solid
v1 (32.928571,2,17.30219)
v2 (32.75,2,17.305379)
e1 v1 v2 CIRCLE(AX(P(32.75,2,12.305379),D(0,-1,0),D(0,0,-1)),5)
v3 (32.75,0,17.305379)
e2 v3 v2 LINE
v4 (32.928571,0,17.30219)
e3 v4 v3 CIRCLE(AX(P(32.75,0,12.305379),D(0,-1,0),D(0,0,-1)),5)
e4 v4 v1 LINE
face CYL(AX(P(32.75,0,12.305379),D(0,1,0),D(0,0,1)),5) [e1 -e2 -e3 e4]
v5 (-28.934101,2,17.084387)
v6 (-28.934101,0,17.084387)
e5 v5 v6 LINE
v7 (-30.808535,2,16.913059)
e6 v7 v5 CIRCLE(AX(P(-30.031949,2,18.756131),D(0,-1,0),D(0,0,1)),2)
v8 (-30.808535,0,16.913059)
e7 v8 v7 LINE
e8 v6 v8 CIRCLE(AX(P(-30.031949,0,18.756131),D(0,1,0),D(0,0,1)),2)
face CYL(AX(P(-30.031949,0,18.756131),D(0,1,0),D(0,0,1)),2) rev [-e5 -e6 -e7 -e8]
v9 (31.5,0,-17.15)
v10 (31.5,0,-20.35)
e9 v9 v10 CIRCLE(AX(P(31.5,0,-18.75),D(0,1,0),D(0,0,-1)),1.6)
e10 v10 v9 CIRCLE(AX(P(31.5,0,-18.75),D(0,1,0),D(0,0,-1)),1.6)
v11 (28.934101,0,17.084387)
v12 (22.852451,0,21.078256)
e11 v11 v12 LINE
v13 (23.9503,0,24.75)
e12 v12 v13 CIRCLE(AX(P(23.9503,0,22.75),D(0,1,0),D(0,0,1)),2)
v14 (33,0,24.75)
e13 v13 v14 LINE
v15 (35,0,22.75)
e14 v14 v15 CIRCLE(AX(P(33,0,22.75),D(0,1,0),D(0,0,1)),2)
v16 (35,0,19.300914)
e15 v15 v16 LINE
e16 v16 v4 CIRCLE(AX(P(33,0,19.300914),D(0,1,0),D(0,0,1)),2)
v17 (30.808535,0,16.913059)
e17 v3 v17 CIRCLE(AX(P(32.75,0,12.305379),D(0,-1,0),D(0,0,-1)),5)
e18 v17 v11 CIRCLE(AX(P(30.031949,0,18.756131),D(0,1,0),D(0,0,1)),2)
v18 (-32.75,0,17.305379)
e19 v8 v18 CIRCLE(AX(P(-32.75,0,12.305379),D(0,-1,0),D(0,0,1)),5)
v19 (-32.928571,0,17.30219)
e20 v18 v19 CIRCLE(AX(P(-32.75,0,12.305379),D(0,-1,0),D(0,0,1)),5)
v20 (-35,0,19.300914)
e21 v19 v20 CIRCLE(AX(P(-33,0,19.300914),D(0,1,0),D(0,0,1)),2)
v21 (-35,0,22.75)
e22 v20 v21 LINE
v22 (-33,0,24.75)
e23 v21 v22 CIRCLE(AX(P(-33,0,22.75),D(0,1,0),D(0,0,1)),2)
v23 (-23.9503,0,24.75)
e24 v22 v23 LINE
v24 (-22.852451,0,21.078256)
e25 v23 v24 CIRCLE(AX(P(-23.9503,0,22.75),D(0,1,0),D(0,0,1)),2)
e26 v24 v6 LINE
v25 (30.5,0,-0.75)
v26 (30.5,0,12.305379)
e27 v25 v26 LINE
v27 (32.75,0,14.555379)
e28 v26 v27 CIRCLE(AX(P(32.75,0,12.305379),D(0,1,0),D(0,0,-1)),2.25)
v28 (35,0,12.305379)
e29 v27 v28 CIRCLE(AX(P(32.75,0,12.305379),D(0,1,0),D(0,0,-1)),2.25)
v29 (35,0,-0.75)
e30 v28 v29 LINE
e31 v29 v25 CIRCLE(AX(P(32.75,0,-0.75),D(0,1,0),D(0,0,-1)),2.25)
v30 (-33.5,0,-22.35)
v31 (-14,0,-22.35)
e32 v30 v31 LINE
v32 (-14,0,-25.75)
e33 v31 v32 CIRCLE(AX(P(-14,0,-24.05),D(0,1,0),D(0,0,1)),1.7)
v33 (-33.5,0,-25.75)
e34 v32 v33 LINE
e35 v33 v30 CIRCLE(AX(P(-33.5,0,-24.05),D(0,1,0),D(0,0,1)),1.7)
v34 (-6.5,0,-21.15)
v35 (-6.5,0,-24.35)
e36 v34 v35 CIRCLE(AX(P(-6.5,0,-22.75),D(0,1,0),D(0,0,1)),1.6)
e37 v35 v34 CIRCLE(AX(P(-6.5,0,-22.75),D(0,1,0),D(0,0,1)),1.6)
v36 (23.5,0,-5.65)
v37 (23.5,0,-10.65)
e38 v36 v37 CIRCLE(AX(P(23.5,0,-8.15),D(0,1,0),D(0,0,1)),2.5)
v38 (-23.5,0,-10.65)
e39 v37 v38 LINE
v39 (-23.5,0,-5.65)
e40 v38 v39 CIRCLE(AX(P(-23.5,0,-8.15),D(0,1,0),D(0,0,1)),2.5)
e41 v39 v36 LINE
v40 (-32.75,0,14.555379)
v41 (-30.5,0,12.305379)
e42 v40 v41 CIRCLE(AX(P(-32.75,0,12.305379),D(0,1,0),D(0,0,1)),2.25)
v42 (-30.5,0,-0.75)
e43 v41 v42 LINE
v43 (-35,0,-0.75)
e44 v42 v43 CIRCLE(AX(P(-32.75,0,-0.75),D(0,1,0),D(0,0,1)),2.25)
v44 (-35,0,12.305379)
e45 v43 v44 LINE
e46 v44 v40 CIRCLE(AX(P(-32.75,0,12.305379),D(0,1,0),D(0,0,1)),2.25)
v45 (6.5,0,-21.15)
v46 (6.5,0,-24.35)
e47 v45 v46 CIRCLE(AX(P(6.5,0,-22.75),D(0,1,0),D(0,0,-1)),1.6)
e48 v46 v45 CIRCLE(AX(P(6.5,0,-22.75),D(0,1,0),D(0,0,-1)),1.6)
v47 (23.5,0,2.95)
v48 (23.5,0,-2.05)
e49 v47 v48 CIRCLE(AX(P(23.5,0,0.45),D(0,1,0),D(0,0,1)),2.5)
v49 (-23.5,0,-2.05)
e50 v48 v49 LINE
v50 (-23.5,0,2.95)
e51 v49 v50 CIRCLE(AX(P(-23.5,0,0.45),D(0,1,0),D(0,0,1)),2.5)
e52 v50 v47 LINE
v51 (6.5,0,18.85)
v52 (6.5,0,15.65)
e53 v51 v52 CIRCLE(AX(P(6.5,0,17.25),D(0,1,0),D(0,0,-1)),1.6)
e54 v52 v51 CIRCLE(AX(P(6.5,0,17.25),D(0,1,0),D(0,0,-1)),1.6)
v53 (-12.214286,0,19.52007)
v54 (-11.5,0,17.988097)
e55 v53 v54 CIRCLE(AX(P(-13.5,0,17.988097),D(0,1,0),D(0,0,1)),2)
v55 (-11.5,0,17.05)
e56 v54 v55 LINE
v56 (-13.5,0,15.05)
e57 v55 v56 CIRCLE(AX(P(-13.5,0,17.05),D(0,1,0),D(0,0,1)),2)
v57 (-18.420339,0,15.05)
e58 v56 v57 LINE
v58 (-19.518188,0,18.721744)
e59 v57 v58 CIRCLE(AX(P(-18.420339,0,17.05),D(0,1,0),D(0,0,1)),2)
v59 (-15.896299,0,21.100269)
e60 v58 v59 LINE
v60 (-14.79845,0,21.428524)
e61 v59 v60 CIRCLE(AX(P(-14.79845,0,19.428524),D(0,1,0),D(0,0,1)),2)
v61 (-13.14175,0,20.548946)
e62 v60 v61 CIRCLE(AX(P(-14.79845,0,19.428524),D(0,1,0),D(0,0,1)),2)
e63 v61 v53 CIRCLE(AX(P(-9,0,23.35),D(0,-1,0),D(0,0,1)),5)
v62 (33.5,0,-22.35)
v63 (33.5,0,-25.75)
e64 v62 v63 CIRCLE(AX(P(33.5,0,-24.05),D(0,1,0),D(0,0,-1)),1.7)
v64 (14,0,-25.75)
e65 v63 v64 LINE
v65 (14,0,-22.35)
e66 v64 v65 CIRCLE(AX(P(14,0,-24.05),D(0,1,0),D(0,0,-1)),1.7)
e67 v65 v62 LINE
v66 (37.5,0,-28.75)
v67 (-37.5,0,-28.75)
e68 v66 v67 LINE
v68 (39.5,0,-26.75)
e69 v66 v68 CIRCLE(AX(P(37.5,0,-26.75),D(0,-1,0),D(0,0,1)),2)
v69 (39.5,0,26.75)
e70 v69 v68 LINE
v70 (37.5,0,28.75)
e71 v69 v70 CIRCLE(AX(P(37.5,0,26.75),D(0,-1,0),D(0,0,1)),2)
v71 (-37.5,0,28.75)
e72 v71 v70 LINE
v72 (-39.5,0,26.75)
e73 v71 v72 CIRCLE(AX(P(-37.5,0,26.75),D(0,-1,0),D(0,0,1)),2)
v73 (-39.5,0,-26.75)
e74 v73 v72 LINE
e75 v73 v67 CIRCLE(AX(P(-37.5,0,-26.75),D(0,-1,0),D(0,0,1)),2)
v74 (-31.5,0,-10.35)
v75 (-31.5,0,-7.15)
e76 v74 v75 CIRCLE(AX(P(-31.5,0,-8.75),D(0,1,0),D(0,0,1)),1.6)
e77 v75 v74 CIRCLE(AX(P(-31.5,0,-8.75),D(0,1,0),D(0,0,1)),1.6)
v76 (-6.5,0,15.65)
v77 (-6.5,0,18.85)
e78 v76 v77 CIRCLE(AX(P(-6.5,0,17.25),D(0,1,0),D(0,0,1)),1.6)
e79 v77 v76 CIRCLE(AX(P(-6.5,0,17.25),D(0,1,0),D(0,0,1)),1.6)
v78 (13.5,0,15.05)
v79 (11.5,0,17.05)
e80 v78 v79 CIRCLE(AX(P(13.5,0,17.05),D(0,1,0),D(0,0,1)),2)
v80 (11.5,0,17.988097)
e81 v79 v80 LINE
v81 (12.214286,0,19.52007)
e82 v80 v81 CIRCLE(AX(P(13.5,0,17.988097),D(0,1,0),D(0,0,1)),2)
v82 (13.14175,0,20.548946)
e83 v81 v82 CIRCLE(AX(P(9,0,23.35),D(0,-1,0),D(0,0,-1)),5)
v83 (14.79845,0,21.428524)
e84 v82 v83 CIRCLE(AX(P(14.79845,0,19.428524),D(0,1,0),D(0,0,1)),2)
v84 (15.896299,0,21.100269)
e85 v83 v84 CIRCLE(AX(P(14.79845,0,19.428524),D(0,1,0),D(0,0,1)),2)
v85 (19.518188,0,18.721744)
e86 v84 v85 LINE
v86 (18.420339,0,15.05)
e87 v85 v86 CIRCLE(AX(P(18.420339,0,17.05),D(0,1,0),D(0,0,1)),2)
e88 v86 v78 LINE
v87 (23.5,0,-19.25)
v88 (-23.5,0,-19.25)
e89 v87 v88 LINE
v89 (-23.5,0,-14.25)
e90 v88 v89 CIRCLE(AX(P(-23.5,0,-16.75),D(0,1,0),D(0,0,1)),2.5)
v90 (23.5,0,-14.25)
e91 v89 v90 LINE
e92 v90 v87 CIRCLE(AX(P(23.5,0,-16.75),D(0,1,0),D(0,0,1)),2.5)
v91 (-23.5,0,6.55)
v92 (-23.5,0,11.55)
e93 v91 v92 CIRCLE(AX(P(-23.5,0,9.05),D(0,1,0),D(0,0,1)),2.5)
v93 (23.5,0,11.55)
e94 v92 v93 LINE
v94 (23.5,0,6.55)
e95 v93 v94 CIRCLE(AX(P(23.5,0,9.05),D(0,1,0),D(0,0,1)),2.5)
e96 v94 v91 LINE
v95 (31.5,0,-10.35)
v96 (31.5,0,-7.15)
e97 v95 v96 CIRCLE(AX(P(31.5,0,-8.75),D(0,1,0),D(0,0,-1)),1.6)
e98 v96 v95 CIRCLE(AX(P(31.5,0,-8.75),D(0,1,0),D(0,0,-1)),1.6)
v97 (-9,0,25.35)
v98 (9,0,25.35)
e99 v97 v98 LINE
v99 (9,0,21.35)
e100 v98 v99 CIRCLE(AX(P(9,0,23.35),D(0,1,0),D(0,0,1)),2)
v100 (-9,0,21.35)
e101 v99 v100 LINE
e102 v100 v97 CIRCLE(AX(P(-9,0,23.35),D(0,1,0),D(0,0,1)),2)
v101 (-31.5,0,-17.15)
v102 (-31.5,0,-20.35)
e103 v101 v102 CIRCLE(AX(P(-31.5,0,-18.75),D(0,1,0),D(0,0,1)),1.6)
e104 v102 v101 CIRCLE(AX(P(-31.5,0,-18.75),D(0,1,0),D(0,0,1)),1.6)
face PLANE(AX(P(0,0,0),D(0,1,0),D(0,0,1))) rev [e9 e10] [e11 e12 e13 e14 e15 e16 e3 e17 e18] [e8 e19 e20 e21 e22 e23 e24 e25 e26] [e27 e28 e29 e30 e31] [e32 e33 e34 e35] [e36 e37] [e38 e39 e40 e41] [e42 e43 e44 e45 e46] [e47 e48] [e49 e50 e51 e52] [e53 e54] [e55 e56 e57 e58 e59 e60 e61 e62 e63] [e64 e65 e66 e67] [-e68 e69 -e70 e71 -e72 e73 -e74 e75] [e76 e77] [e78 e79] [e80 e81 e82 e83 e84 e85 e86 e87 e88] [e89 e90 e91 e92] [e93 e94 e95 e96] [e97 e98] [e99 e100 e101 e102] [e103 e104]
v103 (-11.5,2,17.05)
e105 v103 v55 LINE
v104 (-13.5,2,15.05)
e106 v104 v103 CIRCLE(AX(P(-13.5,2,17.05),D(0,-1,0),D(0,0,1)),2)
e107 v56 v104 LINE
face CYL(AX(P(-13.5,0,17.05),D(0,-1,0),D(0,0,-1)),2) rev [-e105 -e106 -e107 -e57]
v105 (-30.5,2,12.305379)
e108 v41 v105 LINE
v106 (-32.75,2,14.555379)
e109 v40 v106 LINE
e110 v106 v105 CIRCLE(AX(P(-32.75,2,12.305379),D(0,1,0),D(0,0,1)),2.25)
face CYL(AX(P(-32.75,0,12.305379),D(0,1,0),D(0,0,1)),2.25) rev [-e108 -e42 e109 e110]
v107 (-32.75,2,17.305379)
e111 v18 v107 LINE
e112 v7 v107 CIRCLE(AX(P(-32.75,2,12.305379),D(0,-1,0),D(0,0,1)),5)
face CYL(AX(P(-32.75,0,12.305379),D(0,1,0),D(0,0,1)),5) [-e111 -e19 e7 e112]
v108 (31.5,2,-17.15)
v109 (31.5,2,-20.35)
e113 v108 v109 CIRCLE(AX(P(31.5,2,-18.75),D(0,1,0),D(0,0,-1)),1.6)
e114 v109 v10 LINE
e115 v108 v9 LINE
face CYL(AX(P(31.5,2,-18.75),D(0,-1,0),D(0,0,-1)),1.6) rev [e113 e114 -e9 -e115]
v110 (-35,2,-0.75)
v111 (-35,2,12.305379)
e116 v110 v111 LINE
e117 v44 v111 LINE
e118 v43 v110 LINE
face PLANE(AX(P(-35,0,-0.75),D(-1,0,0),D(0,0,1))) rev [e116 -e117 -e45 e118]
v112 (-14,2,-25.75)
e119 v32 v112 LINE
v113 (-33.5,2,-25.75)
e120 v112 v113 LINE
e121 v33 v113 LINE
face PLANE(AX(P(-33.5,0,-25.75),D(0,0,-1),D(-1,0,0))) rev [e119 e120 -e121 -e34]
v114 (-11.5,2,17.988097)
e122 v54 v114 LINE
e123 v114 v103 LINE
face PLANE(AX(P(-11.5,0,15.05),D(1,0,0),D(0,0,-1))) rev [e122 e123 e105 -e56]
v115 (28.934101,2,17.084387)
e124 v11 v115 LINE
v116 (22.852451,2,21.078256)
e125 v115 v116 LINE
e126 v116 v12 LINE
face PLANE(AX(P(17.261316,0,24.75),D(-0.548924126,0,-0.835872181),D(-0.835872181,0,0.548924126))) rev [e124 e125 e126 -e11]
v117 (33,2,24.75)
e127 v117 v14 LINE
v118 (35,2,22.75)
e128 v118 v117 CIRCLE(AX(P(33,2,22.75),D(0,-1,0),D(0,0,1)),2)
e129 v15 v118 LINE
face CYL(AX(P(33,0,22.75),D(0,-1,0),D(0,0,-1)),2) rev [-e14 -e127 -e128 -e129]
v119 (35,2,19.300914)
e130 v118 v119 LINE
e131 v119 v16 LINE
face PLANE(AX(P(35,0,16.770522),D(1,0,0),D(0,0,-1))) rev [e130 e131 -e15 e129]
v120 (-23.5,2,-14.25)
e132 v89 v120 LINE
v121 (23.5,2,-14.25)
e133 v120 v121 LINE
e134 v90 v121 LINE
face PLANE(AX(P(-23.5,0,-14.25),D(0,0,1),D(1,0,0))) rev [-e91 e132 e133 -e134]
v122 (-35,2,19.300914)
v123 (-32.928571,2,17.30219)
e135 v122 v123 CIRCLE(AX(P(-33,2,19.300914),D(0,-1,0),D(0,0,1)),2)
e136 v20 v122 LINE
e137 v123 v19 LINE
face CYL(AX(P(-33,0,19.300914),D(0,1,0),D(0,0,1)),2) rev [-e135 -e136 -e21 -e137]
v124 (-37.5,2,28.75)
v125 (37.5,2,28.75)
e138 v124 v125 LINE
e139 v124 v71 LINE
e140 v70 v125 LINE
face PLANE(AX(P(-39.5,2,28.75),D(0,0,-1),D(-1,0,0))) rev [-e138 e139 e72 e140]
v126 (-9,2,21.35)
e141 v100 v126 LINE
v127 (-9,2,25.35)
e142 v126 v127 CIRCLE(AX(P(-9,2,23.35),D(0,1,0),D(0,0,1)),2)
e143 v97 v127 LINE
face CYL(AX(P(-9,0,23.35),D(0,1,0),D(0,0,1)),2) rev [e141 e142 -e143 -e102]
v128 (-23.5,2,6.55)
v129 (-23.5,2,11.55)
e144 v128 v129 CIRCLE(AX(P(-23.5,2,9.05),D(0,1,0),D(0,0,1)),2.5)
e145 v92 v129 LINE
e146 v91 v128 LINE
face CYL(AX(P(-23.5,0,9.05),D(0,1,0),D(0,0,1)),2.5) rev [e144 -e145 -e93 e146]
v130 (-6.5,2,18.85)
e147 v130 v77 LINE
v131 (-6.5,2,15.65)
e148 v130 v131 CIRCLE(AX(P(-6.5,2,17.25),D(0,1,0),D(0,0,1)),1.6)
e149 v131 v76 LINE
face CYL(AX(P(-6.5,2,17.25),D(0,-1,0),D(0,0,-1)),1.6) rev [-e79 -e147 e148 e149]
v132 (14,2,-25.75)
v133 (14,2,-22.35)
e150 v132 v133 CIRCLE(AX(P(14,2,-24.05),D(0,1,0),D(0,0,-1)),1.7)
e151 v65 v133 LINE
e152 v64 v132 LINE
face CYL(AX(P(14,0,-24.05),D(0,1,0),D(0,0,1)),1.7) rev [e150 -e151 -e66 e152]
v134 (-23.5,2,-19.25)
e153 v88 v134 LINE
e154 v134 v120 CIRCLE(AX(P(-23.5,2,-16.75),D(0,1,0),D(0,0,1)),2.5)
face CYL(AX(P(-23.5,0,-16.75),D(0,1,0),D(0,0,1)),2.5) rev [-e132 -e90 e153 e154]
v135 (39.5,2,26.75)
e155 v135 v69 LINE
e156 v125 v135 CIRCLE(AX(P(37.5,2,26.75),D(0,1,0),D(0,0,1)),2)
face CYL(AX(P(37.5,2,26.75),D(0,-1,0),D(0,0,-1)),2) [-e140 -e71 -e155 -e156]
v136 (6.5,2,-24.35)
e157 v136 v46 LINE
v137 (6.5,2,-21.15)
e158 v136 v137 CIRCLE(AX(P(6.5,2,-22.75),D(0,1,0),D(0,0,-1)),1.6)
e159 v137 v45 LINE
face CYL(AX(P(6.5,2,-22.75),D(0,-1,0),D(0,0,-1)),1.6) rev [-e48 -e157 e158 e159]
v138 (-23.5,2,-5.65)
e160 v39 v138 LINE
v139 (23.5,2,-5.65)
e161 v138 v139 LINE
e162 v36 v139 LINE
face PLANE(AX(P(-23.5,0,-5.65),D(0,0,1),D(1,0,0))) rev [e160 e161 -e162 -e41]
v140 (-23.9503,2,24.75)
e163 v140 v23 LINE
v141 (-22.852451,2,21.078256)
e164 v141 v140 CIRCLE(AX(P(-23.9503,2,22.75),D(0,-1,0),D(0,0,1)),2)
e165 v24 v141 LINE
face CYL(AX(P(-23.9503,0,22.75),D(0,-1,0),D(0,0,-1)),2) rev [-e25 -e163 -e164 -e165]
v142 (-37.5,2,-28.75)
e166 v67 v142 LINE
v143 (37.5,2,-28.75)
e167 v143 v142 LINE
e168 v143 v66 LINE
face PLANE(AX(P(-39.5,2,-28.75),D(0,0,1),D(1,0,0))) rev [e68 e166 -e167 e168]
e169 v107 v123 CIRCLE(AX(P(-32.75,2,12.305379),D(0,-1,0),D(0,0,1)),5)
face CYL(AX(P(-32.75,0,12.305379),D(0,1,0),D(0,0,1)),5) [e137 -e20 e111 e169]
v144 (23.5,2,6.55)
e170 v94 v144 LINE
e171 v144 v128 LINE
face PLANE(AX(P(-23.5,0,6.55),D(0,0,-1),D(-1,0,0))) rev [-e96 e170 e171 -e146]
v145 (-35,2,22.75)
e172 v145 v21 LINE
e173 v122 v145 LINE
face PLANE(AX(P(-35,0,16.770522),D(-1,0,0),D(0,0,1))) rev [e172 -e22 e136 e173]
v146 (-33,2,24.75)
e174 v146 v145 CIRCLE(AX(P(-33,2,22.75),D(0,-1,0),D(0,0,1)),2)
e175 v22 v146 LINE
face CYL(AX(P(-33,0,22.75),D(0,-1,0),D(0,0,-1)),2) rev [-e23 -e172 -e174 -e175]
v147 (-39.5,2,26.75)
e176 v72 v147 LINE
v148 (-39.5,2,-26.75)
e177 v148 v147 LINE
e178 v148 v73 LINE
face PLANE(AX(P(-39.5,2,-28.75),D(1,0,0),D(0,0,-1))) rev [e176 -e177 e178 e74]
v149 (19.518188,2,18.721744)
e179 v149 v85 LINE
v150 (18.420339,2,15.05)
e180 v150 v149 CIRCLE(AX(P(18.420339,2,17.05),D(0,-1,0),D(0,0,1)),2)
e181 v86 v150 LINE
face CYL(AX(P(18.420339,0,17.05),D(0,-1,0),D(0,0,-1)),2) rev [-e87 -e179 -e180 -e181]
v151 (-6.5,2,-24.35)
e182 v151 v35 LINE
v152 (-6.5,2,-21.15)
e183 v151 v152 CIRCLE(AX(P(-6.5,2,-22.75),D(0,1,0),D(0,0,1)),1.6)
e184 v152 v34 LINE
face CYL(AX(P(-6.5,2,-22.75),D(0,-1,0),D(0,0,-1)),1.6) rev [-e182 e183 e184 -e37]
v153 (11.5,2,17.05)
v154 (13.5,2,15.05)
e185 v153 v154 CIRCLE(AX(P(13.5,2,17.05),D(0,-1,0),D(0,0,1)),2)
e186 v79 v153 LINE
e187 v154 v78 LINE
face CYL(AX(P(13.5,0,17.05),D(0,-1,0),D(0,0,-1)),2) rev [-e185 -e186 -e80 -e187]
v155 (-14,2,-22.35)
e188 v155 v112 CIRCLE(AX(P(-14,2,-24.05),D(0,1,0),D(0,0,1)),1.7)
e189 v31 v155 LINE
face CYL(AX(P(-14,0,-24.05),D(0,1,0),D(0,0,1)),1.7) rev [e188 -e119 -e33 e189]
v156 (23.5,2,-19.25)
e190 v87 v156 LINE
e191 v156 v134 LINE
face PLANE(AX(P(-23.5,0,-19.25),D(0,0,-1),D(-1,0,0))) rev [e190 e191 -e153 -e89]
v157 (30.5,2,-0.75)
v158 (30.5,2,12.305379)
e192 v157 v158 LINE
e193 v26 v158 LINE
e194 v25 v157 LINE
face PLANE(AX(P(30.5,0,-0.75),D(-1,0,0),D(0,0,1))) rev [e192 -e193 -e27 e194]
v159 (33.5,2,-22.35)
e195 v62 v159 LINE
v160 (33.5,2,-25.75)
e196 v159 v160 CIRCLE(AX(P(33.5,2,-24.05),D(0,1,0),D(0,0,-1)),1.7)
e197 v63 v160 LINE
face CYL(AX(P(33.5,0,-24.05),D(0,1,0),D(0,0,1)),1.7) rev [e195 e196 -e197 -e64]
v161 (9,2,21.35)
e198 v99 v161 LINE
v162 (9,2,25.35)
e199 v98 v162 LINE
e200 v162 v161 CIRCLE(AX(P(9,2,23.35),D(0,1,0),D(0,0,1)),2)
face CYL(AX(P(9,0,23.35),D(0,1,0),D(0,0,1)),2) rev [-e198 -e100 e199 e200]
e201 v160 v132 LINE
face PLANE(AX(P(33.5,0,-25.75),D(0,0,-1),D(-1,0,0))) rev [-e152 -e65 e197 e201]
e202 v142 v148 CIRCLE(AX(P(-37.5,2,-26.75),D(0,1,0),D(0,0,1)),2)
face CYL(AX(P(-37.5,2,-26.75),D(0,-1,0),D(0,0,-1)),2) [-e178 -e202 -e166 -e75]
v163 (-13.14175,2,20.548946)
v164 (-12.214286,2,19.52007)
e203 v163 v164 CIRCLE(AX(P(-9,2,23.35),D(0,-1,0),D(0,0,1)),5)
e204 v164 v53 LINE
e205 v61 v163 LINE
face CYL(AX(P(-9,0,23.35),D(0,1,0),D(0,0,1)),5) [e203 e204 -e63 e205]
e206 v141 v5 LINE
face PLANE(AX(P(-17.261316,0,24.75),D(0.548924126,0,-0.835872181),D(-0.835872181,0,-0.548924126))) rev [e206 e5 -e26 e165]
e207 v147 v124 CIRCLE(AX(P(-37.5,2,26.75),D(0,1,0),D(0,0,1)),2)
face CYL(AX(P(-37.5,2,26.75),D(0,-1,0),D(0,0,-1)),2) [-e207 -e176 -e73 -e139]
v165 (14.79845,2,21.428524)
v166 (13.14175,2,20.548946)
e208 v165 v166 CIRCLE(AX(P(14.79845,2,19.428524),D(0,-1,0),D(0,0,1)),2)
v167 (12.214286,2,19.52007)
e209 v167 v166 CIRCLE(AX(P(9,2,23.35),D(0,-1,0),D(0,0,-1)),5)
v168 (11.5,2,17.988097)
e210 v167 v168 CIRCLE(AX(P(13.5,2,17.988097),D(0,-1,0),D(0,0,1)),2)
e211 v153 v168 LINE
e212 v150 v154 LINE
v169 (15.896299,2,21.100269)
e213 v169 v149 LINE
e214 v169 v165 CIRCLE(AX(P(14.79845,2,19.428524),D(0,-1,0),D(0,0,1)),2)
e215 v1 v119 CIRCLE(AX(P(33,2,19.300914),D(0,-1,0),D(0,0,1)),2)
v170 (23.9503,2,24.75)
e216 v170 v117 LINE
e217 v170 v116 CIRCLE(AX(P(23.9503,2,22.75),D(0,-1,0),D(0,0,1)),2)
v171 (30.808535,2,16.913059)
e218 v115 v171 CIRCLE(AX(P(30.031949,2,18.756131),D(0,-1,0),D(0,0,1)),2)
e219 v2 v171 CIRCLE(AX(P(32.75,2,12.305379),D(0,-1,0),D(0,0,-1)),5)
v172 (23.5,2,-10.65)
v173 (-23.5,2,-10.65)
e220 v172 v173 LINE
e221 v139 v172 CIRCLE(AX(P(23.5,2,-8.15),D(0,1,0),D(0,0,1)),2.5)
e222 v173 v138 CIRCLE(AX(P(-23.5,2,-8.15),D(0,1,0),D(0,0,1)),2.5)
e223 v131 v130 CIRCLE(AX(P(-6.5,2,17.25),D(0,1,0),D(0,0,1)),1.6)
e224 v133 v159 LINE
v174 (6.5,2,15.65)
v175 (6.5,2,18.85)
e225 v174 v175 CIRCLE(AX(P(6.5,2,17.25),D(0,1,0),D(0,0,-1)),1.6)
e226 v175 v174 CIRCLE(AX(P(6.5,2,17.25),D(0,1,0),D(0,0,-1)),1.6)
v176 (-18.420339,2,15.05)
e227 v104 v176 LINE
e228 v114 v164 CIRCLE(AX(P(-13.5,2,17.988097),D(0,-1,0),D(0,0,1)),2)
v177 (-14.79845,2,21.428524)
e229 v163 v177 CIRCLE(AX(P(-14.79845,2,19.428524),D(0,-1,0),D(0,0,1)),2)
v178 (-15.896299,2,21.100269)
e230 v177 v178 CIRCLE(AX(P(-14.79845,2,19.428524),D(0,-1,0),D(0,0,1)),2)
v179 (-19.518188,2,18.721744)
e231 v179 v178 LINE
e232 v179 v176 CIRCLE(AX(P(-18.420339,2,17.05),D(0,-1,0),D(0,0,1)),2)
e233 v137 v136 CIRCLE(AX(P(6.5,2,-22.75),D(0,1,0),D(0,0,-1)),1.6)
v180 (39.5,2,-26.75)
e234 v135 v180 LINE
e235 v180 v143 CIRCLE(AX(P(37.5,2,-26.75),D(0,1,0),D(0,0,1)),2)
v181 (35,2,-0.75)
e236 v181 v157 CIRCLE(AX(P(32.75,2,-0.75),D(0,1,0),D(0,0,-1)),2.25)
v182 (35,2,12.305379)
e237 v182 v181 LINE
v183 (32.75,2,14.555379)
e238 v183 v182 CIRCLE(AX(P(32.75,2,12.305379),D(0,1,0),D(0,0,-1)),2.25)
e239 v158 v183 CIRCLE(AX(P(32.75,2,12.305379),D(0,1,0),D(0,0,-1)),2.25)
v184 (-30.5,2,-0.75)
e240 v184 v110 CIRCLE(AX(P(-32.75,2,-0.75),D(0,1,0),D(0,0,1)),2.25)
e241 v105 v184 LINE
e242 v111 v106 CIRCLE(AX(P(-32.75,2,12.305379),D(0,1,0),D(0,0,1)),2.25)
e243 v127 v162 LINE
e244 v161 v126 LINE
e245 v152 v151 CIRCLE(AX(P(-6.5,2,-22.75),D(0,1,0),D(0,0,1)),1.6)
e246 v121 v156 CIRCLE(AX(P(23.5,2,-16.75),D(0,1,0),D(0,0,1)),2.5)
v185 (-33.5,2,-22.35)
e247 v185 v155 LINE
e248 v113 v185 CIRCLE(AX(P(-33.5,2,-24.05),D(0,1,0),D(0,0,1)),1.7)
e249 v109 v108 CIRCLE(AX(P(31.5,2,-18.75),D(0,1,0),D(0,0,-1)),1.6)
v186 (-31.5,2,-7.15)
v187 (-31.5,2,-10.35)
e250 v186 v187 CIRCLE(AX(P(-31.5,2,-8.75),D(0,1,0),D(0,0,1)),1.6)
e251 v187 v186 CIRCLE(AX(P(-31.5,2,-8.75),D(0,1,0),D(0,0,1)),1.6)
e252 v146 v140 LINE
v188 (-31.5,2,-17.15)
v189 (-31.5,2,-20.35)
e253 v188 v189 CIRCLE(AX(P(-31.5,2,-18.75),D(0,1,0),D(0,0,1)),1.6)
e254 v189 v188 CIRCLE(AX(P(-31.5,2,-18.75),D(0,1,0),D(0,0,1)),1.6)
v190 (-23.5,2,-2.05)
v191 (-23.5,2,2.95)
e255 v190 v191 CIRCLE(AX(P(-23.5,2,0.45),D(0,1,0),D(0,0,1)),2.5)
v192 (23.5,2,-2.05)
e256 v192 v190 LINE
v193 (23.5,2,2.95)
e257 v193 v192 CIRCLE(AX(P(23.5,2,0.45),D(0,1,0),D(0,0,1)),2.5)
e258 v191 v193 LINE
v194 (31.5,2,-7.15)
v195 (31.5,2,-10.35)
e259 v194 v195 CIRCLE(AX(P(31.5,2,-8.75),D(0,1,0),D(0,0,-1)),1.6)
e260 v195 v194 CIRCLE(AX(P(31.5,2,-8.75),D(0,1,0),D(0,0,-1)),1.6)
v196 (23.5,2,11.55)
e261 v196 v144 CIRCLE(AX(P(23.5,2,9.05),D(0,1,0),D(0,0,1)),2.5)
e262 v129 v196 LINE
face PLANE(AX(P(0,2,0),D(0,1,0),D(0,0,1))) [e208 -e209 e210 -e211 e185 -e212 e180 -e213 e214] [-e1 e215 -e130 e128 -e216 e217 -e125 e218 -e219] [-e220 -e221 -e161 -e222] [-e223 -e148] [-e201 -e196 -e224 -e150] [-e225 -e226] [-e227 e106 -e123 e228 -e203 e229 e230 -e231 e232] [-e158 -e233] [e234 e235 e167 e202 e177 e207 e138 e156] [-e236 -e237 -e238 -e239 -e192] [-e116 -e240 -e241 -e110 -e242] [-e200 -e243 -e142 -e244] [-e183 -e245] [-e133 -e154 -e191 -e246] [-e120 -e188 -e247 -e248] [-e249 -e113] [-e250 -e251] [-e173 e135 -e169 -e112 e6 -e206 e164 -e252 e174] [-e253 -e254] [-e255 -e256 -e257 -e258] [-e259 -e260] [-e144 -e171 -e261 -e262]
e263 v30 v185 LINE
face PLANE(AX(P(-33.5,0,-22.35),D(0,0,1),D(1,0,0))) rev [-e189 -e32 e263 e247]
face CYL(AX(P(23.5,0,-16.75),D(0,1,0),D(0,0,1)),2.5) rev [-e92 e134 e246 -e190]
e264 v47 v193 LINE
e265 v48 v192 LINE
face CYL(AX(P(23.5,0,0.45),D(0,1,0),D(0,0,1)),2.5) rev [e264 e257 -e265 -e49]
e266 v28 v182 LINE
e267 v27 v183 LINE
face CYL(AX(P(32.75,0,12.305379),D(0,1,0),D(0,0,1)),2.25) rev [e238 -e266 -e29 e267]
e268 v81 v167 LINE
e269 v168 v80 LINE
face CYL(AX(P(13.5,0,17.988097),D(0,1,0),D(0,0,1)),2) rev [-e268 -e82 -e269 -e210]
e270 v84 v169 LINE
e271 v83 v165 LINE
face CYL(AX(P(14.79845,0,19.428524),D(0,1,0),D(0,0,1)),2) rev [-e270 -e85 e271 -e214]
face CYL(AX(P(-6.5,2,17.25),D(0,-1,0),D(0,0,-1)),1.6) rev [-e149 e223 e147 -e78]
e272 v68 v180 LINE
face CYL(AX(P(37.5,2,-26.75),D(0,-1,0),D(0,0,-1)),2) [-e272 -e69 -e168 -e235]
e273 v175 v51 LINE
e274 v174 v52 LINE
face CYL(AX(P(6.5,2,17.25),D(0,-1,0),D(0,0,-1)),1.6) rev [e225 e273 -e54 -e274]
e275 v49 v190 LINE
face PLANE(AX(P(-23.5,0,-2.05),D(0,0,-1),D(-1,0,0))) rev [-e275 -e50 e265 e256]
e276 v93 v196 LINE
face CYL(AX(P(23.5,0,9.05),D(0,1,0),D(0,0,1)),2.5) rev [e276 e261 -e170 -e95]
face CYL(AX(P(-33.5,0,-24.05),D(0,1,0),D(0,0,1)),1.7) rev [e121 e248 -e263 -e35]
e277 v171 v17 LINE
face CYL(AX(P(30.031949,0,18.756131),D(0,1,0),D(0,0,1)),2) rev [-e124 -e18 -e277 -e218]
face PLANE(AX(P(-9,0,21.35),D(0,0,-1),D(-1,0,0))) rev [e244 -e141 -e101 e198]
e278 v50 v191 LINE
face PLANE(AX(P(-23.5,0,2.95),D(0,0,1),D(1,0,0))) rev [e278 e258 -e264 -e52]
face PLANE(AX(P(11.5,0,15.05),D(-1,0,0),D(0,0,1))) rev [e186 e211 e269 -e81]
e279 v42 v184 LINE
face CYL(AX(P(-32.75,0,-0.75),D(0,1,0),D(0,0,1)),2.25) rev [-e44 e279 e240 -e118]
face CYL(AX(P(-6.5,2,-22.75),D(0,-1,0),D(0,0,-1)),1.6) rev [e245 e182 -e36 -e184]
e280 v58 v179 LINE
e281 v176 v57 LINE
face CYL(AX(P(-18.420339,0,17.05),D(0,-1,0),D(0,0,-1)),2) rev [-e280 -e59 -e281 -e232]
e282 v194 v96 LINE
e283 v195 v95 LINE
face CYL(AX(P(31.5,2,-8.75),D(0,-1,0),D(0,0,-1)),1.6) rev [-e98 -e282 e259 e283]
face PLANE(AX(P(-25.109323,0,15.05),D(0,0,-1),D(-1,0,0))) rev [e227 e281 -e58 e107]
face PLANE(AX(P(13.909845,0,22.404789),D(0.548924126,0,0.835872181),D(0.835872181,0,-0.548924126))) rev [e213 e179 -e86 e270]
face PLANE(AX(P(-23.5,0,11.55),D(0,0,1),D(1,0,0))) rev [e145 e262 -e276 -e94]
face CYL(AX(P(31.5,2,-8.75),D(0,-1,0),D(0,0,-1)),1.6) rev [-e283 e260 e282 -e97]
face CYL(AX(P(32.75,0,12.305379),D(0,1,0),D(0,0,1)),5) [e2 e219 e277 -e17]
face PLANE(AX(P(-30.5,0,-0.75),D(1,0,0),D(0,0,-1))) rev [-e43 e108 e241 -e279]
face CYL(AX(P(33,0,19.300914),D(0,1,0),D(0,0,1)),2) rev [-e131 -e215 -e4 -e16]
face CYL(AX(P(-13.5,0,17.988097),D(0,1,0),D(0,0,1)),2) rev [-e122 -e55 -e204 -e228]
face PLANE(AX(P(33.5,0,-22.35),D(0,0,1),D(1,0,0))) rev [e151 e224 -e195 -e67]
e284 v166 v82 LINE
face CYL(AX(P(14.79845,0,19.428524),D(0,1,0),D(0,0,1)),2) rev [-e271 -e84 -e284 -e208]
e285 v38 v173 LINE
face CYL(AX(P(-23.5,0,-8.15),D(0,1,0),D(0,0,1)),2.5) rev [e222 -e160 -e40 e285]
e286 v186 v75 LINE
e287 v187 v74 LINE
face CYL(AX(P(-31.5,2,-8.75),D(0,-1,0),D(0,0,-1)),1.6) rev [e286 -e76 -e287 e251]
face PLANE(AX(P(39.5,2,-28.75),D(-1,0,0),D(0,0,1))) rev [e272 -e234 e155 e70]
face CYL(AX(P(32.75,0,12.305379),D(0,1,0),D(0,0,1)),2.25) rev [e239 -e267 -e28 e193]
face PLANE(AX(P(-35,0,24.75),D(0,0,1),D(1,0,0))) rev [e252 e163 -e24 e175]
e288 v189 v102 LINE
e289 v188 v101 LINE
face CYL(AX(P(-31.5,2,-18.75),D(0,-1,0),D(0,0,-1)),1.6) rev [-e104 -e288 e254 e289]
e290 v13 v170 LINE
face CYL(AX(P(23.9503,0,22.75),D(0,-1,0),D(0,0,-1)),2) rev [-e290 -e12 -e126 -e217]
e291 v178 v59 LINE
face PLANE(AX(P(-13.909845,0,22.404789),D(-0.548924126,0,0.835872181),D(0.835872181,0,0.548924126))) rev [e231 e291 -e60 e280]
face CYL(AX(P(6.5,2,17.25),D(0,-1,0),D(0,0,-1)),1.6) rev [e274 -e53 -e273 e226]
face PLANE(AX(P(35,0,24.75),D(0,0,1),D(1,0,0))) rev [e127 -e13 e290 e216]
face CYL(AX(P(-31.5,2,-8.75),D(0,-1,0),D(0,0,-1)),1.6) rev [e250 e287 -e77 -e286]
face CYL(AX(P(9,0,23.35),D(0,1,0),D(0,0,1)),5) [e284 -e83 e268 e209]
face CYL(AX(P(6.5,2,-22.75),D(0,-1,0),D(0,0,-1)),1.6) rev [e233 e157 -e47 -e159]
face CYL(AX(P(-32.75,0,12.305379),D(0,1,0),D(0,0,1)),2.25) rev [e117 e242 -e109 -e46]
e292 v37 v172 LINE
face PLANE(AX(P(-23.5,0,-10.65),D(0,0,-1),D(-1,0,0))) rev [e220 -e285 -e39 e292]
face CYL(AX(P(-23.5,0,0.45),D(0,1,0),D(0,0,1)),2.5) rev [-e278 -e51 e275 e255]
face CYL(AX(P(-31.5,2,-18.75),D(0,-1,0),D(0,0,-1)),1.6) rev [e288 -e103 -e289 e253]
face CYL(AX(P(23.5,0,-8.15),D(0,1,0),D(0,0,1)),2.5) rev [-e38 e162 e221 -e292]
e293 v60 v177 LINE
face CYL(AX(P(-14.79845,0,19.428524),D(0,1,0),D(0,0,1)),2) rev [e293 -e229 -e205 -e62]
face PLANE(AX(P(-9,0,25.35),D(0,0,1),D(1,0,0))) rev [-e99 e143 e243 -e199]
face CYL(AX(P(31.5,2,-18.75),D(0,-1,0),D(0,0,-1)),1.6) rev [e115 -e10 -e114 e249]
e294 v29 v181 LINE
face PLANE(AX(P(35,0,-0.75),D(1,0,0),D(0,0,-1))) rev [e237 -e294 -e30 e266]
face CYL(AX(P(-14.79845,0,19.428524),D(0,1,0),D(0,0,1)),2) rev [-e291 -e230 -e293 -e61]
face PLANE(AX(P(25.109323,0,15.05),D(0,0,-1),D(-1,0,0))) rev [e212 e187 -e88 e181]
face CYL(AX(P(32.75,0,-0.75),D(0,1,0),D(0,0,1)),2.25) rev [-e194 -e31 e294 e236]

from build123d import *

# Parameters (mm, degrees)
SKETCH1_W           = 79
SKETCH1_H           = 57.5
SKETCH1_R           = 1.6
BOSS_EXTRUDE1_DEPTH = 2
CUT_EXTRUDE1_DEPTH  = 49.895935414
R2_FILLET_1_R       = 2


with BuildPart() as part:
    # Sketch1 → Boss-Extrude1 (new body)
    with BuildSketch(Plane(origin=(0, 0, 0), x_dir=(1, 0, 0), z_dir=(0, 1, 0))):
        Rectangle(SKETCH1_W, SKETCH1_H)
        with Locations(Location((-31.5, 18.75, 0), (0, 0, 270))):
            Circle(SKETCH1_R, mode=Mode.SUBTRACT)
        with Locations(Location((-31.5, 8.75, 0), (0, 0, 270))):
            Circle(SKETCH1_R, mode=Mode.SUBTRACT)
        with Locations(Location((31.5, 8.75, 0), (0, 0, 90))):
            Circle(SKETCH1_R, mode=Mode.SUBTRACT)
        with Locations(Location((31.5, 18.75, 0), (0, 0, 90))):
            Circle(SKETCH1_R, mode=Mode.SUBTRACT)
        with Locations(Location((-6.5, 22.75, 0), (0, 0, 270))):
            Circle(SKETCH1_R, mode=Mode.SUBTRACT)
        with Locations(Location((-6.5, -17.25, 0), (0, 0, 270))):
            Circle(SKETCH1_R, mode=Mode.SUBTRACT)
        with Locations(Location((6.5, 22.75, 0), (0, 0, 90))):
            Circle(SKETCH1_R, mode=Mode.SUBTRACT)
        with Locations(Location((6.5, -17.25, 0), (0, 0, 90))):
            Circle(SKETCH1_R, mode=Mode.SUBTRACT)
    extrude(amount=BOSS_EXTRUDE1_DEPTH)

    # Sketch2 → Cut-Extrude1 (cut, through all)
    with BuildSketch(Plane(origin=(0, 2, 0), x_dir=(1, 0, 0), z_dir=(0, 1, 0))):
        with BuildLine():
            Line((-23.5, 19.25), (23.5, 19.25))
            ThreePointArc((23.5, 19.25), (26, 16.75), (23.5, 14.25))
            Line((23.5, 14.25), (-23.5, 14.25))
            ThreePointArc((-23.5, 14.25), (-26, 16.75), (-23.5, 19.25))
        make_face()
        with BuildLine():
            Line((-23.5, 10.65), (23.5, 10.65))
            ThreePointArc((23.5, 10.65), (26, 8.15), (23.5, 5.65))
            Line((23.5, 5.65), (-23.5, 5.65))
            ThreePointArc((-23.5, 5.65), (-26, 8.15), (-23.5, 10.65))
        make_face()
        with BuildLine():
            Line((-23.5, 2.05), (23.5, 2.05))
            ThreePointArc((23.5, 2.05), (26, -0.45), (23.5, -2.95))
            Line((23.5, -2.95), (-23.5, -2.95))
            ThreePointArc((-23.5, -2.95), (-26, -0.45), (-23.5, 2.05))
        make_face()
        with BuildLine():
            Line((-23.5, -6.55), (23.5, -6.55))
            ThreePointArc((23.5, -6.55), (26, -9.05), (23.5, -11.55))
            Line((23.5, -11.55), (-23.5, -11.55))
            ThreePointArc((-23.5, -11.55), (-26, -9.05), (-23.5, -6.55))
        make_face()
        with BuildLine():
            Line((-33.5, 25.75), (-14, 25.75))
            ThreePointArc((-14, 25.75), (-12.3, 24.05), (-14, 22.35))
            Line((-14, 22.35), (-33.5, 22.35))
            ThreePointArc((-33.5, 22.35), (-35.2, 24.05), (-33.5, 25.75))
        make_face()
        with BuildLine():
            Line((33.5, 25.75), (14, 25.75))
            ThreePointArc((14, 25.75), (12.3, 24.05), (14, 22.35))
            Line((14, 22.35), (33.5, 22.35))
            ThreePointArc((33.5, 22.35), (35.2, 24.05), (33.5, 25.75))
        make_face()
        with BuildLine():
            Line((-9, -21.35), (9, -21.35))
            ThreePointArc((9, -21.35), (11, -23.35), (9, -25.35))
            Line((9, -25.35), (-9, -25.35))
            ThreePointArc((-9, -25.35), (-11, -23.35), (-9, -21.35))
        make_face()
        with BuildLine():
            Line((-30.5, 0.75), (-30.5, -12.305379368))
            ThreePointArc((-30.5, -12.305379368), (-32.75, -14.555379368), (-35, -12.305379368))
            Line((-35, -12.305379368), (-35, 0.75))
            ThreePointArc((-35, 0.75), (-32.75, 3), (-30.5, 0.75))
        make_face()
        with BuildLine():
            Line((30.5, 0.75), (30.5, -12.305379368))
            ThreePointArc((30.5, -12.305379368), (32.75, -14.555379368), (35, -12.305379368))
            Line((35, -12.305379368), (35, 0.75))
            ThreePointArc((35, 0.75), (32.75, 3), (30.5, 0.75))
        make_face()
        with BuildLine():
            Line((-35, -16.770522143), (-35, -24.75))
            Line((-35, -24.75), (-17.261316253, -24.75))
            Line((-17.261316253, -24.75), (-29.927103479, -16.432273507))
            ThreePointArc((-29.927103479, -16.432273507), (-32.417350574, -17.294301533), (-35, -16.770522143))
        make_face()
        with BuildLine():
            Line((-25.10932284, -15.05), (-11.5, -15.05))
            Line((-11.5, -15.05), (-11.5, -19.019872981))
            ThreePointArc((-11.5, -19.019872981), (-13.073188505, -20.450149072), (-13.909844854, -22.404789172))
            Line((-13.909844854, -22.404789172), (-25.10932284, -15.05))
        make_face()
        with BuildLine():
            Line((17.261316253, -24.75), (29.927103479, -16.432273507))
            ThreePointArc((29.927103479, -16.432273507), (32.417350574, -17.294301533), (35, -16.770522143))
            Line((35, -16.770522143), (35, -24.75))
            Line((35, -24.75), (17.261316253, -24.75))
        make_face()
        with BuildLine():
            Line((25.10932284, -15.05), (11.5, -15.05))
            Line((11.5, -15.05), (11.5, -19.019872981))
            ThreePointArc((11.5, -19.019872981), (13.073188505, -20.450149072), (13.909844854, -22.404789172))
            Line((13.909844854, -22.404789172), (25.10932284, -15.05))
        make_face()
    extrude(amount=-CUT_EXTRUDE1_DEPTH, mode=Mode.SUBTRACT)

    # R2 Fillet 1
    r2_fillet_1_edges = [part.edges().sort_by_distance(p)[0] for p in [
        (-11.5, 1, 15.05),
        (-11.5, 1, 19.019872981),
        (-13.909844854, 1, 22.404789172),
        (-25.10932284, 1, 15.05),
        (-35, 1, 16.770522143),
        (-29.927103479, 1, 16.432273507),
        (-17.261316253, 1, 24.75),
        (-35, 1, 24.75),
        (25.10932284, 1, 15.05),
        (13.909844854, 1, 22.404789172),
        (11.5, 1, 19.019872981),
        (11.5, 1, 15.05),
        (29.927103479, 1, 16.432273507),
        (35, 1, 16.770522143),
        (35, 1, 24.75),
        (17.261316253, 1, 24.75),
        (39.5, 1, 28.75),
        (-39.5, 1, 28.75),
        (-39.5, 1, -28.75),
        (39.5, 1, -28.75),
    ]]
    fillet(r2_fillet_1_edges, radius=R2_FILLET_1_R)


solid = part.part
